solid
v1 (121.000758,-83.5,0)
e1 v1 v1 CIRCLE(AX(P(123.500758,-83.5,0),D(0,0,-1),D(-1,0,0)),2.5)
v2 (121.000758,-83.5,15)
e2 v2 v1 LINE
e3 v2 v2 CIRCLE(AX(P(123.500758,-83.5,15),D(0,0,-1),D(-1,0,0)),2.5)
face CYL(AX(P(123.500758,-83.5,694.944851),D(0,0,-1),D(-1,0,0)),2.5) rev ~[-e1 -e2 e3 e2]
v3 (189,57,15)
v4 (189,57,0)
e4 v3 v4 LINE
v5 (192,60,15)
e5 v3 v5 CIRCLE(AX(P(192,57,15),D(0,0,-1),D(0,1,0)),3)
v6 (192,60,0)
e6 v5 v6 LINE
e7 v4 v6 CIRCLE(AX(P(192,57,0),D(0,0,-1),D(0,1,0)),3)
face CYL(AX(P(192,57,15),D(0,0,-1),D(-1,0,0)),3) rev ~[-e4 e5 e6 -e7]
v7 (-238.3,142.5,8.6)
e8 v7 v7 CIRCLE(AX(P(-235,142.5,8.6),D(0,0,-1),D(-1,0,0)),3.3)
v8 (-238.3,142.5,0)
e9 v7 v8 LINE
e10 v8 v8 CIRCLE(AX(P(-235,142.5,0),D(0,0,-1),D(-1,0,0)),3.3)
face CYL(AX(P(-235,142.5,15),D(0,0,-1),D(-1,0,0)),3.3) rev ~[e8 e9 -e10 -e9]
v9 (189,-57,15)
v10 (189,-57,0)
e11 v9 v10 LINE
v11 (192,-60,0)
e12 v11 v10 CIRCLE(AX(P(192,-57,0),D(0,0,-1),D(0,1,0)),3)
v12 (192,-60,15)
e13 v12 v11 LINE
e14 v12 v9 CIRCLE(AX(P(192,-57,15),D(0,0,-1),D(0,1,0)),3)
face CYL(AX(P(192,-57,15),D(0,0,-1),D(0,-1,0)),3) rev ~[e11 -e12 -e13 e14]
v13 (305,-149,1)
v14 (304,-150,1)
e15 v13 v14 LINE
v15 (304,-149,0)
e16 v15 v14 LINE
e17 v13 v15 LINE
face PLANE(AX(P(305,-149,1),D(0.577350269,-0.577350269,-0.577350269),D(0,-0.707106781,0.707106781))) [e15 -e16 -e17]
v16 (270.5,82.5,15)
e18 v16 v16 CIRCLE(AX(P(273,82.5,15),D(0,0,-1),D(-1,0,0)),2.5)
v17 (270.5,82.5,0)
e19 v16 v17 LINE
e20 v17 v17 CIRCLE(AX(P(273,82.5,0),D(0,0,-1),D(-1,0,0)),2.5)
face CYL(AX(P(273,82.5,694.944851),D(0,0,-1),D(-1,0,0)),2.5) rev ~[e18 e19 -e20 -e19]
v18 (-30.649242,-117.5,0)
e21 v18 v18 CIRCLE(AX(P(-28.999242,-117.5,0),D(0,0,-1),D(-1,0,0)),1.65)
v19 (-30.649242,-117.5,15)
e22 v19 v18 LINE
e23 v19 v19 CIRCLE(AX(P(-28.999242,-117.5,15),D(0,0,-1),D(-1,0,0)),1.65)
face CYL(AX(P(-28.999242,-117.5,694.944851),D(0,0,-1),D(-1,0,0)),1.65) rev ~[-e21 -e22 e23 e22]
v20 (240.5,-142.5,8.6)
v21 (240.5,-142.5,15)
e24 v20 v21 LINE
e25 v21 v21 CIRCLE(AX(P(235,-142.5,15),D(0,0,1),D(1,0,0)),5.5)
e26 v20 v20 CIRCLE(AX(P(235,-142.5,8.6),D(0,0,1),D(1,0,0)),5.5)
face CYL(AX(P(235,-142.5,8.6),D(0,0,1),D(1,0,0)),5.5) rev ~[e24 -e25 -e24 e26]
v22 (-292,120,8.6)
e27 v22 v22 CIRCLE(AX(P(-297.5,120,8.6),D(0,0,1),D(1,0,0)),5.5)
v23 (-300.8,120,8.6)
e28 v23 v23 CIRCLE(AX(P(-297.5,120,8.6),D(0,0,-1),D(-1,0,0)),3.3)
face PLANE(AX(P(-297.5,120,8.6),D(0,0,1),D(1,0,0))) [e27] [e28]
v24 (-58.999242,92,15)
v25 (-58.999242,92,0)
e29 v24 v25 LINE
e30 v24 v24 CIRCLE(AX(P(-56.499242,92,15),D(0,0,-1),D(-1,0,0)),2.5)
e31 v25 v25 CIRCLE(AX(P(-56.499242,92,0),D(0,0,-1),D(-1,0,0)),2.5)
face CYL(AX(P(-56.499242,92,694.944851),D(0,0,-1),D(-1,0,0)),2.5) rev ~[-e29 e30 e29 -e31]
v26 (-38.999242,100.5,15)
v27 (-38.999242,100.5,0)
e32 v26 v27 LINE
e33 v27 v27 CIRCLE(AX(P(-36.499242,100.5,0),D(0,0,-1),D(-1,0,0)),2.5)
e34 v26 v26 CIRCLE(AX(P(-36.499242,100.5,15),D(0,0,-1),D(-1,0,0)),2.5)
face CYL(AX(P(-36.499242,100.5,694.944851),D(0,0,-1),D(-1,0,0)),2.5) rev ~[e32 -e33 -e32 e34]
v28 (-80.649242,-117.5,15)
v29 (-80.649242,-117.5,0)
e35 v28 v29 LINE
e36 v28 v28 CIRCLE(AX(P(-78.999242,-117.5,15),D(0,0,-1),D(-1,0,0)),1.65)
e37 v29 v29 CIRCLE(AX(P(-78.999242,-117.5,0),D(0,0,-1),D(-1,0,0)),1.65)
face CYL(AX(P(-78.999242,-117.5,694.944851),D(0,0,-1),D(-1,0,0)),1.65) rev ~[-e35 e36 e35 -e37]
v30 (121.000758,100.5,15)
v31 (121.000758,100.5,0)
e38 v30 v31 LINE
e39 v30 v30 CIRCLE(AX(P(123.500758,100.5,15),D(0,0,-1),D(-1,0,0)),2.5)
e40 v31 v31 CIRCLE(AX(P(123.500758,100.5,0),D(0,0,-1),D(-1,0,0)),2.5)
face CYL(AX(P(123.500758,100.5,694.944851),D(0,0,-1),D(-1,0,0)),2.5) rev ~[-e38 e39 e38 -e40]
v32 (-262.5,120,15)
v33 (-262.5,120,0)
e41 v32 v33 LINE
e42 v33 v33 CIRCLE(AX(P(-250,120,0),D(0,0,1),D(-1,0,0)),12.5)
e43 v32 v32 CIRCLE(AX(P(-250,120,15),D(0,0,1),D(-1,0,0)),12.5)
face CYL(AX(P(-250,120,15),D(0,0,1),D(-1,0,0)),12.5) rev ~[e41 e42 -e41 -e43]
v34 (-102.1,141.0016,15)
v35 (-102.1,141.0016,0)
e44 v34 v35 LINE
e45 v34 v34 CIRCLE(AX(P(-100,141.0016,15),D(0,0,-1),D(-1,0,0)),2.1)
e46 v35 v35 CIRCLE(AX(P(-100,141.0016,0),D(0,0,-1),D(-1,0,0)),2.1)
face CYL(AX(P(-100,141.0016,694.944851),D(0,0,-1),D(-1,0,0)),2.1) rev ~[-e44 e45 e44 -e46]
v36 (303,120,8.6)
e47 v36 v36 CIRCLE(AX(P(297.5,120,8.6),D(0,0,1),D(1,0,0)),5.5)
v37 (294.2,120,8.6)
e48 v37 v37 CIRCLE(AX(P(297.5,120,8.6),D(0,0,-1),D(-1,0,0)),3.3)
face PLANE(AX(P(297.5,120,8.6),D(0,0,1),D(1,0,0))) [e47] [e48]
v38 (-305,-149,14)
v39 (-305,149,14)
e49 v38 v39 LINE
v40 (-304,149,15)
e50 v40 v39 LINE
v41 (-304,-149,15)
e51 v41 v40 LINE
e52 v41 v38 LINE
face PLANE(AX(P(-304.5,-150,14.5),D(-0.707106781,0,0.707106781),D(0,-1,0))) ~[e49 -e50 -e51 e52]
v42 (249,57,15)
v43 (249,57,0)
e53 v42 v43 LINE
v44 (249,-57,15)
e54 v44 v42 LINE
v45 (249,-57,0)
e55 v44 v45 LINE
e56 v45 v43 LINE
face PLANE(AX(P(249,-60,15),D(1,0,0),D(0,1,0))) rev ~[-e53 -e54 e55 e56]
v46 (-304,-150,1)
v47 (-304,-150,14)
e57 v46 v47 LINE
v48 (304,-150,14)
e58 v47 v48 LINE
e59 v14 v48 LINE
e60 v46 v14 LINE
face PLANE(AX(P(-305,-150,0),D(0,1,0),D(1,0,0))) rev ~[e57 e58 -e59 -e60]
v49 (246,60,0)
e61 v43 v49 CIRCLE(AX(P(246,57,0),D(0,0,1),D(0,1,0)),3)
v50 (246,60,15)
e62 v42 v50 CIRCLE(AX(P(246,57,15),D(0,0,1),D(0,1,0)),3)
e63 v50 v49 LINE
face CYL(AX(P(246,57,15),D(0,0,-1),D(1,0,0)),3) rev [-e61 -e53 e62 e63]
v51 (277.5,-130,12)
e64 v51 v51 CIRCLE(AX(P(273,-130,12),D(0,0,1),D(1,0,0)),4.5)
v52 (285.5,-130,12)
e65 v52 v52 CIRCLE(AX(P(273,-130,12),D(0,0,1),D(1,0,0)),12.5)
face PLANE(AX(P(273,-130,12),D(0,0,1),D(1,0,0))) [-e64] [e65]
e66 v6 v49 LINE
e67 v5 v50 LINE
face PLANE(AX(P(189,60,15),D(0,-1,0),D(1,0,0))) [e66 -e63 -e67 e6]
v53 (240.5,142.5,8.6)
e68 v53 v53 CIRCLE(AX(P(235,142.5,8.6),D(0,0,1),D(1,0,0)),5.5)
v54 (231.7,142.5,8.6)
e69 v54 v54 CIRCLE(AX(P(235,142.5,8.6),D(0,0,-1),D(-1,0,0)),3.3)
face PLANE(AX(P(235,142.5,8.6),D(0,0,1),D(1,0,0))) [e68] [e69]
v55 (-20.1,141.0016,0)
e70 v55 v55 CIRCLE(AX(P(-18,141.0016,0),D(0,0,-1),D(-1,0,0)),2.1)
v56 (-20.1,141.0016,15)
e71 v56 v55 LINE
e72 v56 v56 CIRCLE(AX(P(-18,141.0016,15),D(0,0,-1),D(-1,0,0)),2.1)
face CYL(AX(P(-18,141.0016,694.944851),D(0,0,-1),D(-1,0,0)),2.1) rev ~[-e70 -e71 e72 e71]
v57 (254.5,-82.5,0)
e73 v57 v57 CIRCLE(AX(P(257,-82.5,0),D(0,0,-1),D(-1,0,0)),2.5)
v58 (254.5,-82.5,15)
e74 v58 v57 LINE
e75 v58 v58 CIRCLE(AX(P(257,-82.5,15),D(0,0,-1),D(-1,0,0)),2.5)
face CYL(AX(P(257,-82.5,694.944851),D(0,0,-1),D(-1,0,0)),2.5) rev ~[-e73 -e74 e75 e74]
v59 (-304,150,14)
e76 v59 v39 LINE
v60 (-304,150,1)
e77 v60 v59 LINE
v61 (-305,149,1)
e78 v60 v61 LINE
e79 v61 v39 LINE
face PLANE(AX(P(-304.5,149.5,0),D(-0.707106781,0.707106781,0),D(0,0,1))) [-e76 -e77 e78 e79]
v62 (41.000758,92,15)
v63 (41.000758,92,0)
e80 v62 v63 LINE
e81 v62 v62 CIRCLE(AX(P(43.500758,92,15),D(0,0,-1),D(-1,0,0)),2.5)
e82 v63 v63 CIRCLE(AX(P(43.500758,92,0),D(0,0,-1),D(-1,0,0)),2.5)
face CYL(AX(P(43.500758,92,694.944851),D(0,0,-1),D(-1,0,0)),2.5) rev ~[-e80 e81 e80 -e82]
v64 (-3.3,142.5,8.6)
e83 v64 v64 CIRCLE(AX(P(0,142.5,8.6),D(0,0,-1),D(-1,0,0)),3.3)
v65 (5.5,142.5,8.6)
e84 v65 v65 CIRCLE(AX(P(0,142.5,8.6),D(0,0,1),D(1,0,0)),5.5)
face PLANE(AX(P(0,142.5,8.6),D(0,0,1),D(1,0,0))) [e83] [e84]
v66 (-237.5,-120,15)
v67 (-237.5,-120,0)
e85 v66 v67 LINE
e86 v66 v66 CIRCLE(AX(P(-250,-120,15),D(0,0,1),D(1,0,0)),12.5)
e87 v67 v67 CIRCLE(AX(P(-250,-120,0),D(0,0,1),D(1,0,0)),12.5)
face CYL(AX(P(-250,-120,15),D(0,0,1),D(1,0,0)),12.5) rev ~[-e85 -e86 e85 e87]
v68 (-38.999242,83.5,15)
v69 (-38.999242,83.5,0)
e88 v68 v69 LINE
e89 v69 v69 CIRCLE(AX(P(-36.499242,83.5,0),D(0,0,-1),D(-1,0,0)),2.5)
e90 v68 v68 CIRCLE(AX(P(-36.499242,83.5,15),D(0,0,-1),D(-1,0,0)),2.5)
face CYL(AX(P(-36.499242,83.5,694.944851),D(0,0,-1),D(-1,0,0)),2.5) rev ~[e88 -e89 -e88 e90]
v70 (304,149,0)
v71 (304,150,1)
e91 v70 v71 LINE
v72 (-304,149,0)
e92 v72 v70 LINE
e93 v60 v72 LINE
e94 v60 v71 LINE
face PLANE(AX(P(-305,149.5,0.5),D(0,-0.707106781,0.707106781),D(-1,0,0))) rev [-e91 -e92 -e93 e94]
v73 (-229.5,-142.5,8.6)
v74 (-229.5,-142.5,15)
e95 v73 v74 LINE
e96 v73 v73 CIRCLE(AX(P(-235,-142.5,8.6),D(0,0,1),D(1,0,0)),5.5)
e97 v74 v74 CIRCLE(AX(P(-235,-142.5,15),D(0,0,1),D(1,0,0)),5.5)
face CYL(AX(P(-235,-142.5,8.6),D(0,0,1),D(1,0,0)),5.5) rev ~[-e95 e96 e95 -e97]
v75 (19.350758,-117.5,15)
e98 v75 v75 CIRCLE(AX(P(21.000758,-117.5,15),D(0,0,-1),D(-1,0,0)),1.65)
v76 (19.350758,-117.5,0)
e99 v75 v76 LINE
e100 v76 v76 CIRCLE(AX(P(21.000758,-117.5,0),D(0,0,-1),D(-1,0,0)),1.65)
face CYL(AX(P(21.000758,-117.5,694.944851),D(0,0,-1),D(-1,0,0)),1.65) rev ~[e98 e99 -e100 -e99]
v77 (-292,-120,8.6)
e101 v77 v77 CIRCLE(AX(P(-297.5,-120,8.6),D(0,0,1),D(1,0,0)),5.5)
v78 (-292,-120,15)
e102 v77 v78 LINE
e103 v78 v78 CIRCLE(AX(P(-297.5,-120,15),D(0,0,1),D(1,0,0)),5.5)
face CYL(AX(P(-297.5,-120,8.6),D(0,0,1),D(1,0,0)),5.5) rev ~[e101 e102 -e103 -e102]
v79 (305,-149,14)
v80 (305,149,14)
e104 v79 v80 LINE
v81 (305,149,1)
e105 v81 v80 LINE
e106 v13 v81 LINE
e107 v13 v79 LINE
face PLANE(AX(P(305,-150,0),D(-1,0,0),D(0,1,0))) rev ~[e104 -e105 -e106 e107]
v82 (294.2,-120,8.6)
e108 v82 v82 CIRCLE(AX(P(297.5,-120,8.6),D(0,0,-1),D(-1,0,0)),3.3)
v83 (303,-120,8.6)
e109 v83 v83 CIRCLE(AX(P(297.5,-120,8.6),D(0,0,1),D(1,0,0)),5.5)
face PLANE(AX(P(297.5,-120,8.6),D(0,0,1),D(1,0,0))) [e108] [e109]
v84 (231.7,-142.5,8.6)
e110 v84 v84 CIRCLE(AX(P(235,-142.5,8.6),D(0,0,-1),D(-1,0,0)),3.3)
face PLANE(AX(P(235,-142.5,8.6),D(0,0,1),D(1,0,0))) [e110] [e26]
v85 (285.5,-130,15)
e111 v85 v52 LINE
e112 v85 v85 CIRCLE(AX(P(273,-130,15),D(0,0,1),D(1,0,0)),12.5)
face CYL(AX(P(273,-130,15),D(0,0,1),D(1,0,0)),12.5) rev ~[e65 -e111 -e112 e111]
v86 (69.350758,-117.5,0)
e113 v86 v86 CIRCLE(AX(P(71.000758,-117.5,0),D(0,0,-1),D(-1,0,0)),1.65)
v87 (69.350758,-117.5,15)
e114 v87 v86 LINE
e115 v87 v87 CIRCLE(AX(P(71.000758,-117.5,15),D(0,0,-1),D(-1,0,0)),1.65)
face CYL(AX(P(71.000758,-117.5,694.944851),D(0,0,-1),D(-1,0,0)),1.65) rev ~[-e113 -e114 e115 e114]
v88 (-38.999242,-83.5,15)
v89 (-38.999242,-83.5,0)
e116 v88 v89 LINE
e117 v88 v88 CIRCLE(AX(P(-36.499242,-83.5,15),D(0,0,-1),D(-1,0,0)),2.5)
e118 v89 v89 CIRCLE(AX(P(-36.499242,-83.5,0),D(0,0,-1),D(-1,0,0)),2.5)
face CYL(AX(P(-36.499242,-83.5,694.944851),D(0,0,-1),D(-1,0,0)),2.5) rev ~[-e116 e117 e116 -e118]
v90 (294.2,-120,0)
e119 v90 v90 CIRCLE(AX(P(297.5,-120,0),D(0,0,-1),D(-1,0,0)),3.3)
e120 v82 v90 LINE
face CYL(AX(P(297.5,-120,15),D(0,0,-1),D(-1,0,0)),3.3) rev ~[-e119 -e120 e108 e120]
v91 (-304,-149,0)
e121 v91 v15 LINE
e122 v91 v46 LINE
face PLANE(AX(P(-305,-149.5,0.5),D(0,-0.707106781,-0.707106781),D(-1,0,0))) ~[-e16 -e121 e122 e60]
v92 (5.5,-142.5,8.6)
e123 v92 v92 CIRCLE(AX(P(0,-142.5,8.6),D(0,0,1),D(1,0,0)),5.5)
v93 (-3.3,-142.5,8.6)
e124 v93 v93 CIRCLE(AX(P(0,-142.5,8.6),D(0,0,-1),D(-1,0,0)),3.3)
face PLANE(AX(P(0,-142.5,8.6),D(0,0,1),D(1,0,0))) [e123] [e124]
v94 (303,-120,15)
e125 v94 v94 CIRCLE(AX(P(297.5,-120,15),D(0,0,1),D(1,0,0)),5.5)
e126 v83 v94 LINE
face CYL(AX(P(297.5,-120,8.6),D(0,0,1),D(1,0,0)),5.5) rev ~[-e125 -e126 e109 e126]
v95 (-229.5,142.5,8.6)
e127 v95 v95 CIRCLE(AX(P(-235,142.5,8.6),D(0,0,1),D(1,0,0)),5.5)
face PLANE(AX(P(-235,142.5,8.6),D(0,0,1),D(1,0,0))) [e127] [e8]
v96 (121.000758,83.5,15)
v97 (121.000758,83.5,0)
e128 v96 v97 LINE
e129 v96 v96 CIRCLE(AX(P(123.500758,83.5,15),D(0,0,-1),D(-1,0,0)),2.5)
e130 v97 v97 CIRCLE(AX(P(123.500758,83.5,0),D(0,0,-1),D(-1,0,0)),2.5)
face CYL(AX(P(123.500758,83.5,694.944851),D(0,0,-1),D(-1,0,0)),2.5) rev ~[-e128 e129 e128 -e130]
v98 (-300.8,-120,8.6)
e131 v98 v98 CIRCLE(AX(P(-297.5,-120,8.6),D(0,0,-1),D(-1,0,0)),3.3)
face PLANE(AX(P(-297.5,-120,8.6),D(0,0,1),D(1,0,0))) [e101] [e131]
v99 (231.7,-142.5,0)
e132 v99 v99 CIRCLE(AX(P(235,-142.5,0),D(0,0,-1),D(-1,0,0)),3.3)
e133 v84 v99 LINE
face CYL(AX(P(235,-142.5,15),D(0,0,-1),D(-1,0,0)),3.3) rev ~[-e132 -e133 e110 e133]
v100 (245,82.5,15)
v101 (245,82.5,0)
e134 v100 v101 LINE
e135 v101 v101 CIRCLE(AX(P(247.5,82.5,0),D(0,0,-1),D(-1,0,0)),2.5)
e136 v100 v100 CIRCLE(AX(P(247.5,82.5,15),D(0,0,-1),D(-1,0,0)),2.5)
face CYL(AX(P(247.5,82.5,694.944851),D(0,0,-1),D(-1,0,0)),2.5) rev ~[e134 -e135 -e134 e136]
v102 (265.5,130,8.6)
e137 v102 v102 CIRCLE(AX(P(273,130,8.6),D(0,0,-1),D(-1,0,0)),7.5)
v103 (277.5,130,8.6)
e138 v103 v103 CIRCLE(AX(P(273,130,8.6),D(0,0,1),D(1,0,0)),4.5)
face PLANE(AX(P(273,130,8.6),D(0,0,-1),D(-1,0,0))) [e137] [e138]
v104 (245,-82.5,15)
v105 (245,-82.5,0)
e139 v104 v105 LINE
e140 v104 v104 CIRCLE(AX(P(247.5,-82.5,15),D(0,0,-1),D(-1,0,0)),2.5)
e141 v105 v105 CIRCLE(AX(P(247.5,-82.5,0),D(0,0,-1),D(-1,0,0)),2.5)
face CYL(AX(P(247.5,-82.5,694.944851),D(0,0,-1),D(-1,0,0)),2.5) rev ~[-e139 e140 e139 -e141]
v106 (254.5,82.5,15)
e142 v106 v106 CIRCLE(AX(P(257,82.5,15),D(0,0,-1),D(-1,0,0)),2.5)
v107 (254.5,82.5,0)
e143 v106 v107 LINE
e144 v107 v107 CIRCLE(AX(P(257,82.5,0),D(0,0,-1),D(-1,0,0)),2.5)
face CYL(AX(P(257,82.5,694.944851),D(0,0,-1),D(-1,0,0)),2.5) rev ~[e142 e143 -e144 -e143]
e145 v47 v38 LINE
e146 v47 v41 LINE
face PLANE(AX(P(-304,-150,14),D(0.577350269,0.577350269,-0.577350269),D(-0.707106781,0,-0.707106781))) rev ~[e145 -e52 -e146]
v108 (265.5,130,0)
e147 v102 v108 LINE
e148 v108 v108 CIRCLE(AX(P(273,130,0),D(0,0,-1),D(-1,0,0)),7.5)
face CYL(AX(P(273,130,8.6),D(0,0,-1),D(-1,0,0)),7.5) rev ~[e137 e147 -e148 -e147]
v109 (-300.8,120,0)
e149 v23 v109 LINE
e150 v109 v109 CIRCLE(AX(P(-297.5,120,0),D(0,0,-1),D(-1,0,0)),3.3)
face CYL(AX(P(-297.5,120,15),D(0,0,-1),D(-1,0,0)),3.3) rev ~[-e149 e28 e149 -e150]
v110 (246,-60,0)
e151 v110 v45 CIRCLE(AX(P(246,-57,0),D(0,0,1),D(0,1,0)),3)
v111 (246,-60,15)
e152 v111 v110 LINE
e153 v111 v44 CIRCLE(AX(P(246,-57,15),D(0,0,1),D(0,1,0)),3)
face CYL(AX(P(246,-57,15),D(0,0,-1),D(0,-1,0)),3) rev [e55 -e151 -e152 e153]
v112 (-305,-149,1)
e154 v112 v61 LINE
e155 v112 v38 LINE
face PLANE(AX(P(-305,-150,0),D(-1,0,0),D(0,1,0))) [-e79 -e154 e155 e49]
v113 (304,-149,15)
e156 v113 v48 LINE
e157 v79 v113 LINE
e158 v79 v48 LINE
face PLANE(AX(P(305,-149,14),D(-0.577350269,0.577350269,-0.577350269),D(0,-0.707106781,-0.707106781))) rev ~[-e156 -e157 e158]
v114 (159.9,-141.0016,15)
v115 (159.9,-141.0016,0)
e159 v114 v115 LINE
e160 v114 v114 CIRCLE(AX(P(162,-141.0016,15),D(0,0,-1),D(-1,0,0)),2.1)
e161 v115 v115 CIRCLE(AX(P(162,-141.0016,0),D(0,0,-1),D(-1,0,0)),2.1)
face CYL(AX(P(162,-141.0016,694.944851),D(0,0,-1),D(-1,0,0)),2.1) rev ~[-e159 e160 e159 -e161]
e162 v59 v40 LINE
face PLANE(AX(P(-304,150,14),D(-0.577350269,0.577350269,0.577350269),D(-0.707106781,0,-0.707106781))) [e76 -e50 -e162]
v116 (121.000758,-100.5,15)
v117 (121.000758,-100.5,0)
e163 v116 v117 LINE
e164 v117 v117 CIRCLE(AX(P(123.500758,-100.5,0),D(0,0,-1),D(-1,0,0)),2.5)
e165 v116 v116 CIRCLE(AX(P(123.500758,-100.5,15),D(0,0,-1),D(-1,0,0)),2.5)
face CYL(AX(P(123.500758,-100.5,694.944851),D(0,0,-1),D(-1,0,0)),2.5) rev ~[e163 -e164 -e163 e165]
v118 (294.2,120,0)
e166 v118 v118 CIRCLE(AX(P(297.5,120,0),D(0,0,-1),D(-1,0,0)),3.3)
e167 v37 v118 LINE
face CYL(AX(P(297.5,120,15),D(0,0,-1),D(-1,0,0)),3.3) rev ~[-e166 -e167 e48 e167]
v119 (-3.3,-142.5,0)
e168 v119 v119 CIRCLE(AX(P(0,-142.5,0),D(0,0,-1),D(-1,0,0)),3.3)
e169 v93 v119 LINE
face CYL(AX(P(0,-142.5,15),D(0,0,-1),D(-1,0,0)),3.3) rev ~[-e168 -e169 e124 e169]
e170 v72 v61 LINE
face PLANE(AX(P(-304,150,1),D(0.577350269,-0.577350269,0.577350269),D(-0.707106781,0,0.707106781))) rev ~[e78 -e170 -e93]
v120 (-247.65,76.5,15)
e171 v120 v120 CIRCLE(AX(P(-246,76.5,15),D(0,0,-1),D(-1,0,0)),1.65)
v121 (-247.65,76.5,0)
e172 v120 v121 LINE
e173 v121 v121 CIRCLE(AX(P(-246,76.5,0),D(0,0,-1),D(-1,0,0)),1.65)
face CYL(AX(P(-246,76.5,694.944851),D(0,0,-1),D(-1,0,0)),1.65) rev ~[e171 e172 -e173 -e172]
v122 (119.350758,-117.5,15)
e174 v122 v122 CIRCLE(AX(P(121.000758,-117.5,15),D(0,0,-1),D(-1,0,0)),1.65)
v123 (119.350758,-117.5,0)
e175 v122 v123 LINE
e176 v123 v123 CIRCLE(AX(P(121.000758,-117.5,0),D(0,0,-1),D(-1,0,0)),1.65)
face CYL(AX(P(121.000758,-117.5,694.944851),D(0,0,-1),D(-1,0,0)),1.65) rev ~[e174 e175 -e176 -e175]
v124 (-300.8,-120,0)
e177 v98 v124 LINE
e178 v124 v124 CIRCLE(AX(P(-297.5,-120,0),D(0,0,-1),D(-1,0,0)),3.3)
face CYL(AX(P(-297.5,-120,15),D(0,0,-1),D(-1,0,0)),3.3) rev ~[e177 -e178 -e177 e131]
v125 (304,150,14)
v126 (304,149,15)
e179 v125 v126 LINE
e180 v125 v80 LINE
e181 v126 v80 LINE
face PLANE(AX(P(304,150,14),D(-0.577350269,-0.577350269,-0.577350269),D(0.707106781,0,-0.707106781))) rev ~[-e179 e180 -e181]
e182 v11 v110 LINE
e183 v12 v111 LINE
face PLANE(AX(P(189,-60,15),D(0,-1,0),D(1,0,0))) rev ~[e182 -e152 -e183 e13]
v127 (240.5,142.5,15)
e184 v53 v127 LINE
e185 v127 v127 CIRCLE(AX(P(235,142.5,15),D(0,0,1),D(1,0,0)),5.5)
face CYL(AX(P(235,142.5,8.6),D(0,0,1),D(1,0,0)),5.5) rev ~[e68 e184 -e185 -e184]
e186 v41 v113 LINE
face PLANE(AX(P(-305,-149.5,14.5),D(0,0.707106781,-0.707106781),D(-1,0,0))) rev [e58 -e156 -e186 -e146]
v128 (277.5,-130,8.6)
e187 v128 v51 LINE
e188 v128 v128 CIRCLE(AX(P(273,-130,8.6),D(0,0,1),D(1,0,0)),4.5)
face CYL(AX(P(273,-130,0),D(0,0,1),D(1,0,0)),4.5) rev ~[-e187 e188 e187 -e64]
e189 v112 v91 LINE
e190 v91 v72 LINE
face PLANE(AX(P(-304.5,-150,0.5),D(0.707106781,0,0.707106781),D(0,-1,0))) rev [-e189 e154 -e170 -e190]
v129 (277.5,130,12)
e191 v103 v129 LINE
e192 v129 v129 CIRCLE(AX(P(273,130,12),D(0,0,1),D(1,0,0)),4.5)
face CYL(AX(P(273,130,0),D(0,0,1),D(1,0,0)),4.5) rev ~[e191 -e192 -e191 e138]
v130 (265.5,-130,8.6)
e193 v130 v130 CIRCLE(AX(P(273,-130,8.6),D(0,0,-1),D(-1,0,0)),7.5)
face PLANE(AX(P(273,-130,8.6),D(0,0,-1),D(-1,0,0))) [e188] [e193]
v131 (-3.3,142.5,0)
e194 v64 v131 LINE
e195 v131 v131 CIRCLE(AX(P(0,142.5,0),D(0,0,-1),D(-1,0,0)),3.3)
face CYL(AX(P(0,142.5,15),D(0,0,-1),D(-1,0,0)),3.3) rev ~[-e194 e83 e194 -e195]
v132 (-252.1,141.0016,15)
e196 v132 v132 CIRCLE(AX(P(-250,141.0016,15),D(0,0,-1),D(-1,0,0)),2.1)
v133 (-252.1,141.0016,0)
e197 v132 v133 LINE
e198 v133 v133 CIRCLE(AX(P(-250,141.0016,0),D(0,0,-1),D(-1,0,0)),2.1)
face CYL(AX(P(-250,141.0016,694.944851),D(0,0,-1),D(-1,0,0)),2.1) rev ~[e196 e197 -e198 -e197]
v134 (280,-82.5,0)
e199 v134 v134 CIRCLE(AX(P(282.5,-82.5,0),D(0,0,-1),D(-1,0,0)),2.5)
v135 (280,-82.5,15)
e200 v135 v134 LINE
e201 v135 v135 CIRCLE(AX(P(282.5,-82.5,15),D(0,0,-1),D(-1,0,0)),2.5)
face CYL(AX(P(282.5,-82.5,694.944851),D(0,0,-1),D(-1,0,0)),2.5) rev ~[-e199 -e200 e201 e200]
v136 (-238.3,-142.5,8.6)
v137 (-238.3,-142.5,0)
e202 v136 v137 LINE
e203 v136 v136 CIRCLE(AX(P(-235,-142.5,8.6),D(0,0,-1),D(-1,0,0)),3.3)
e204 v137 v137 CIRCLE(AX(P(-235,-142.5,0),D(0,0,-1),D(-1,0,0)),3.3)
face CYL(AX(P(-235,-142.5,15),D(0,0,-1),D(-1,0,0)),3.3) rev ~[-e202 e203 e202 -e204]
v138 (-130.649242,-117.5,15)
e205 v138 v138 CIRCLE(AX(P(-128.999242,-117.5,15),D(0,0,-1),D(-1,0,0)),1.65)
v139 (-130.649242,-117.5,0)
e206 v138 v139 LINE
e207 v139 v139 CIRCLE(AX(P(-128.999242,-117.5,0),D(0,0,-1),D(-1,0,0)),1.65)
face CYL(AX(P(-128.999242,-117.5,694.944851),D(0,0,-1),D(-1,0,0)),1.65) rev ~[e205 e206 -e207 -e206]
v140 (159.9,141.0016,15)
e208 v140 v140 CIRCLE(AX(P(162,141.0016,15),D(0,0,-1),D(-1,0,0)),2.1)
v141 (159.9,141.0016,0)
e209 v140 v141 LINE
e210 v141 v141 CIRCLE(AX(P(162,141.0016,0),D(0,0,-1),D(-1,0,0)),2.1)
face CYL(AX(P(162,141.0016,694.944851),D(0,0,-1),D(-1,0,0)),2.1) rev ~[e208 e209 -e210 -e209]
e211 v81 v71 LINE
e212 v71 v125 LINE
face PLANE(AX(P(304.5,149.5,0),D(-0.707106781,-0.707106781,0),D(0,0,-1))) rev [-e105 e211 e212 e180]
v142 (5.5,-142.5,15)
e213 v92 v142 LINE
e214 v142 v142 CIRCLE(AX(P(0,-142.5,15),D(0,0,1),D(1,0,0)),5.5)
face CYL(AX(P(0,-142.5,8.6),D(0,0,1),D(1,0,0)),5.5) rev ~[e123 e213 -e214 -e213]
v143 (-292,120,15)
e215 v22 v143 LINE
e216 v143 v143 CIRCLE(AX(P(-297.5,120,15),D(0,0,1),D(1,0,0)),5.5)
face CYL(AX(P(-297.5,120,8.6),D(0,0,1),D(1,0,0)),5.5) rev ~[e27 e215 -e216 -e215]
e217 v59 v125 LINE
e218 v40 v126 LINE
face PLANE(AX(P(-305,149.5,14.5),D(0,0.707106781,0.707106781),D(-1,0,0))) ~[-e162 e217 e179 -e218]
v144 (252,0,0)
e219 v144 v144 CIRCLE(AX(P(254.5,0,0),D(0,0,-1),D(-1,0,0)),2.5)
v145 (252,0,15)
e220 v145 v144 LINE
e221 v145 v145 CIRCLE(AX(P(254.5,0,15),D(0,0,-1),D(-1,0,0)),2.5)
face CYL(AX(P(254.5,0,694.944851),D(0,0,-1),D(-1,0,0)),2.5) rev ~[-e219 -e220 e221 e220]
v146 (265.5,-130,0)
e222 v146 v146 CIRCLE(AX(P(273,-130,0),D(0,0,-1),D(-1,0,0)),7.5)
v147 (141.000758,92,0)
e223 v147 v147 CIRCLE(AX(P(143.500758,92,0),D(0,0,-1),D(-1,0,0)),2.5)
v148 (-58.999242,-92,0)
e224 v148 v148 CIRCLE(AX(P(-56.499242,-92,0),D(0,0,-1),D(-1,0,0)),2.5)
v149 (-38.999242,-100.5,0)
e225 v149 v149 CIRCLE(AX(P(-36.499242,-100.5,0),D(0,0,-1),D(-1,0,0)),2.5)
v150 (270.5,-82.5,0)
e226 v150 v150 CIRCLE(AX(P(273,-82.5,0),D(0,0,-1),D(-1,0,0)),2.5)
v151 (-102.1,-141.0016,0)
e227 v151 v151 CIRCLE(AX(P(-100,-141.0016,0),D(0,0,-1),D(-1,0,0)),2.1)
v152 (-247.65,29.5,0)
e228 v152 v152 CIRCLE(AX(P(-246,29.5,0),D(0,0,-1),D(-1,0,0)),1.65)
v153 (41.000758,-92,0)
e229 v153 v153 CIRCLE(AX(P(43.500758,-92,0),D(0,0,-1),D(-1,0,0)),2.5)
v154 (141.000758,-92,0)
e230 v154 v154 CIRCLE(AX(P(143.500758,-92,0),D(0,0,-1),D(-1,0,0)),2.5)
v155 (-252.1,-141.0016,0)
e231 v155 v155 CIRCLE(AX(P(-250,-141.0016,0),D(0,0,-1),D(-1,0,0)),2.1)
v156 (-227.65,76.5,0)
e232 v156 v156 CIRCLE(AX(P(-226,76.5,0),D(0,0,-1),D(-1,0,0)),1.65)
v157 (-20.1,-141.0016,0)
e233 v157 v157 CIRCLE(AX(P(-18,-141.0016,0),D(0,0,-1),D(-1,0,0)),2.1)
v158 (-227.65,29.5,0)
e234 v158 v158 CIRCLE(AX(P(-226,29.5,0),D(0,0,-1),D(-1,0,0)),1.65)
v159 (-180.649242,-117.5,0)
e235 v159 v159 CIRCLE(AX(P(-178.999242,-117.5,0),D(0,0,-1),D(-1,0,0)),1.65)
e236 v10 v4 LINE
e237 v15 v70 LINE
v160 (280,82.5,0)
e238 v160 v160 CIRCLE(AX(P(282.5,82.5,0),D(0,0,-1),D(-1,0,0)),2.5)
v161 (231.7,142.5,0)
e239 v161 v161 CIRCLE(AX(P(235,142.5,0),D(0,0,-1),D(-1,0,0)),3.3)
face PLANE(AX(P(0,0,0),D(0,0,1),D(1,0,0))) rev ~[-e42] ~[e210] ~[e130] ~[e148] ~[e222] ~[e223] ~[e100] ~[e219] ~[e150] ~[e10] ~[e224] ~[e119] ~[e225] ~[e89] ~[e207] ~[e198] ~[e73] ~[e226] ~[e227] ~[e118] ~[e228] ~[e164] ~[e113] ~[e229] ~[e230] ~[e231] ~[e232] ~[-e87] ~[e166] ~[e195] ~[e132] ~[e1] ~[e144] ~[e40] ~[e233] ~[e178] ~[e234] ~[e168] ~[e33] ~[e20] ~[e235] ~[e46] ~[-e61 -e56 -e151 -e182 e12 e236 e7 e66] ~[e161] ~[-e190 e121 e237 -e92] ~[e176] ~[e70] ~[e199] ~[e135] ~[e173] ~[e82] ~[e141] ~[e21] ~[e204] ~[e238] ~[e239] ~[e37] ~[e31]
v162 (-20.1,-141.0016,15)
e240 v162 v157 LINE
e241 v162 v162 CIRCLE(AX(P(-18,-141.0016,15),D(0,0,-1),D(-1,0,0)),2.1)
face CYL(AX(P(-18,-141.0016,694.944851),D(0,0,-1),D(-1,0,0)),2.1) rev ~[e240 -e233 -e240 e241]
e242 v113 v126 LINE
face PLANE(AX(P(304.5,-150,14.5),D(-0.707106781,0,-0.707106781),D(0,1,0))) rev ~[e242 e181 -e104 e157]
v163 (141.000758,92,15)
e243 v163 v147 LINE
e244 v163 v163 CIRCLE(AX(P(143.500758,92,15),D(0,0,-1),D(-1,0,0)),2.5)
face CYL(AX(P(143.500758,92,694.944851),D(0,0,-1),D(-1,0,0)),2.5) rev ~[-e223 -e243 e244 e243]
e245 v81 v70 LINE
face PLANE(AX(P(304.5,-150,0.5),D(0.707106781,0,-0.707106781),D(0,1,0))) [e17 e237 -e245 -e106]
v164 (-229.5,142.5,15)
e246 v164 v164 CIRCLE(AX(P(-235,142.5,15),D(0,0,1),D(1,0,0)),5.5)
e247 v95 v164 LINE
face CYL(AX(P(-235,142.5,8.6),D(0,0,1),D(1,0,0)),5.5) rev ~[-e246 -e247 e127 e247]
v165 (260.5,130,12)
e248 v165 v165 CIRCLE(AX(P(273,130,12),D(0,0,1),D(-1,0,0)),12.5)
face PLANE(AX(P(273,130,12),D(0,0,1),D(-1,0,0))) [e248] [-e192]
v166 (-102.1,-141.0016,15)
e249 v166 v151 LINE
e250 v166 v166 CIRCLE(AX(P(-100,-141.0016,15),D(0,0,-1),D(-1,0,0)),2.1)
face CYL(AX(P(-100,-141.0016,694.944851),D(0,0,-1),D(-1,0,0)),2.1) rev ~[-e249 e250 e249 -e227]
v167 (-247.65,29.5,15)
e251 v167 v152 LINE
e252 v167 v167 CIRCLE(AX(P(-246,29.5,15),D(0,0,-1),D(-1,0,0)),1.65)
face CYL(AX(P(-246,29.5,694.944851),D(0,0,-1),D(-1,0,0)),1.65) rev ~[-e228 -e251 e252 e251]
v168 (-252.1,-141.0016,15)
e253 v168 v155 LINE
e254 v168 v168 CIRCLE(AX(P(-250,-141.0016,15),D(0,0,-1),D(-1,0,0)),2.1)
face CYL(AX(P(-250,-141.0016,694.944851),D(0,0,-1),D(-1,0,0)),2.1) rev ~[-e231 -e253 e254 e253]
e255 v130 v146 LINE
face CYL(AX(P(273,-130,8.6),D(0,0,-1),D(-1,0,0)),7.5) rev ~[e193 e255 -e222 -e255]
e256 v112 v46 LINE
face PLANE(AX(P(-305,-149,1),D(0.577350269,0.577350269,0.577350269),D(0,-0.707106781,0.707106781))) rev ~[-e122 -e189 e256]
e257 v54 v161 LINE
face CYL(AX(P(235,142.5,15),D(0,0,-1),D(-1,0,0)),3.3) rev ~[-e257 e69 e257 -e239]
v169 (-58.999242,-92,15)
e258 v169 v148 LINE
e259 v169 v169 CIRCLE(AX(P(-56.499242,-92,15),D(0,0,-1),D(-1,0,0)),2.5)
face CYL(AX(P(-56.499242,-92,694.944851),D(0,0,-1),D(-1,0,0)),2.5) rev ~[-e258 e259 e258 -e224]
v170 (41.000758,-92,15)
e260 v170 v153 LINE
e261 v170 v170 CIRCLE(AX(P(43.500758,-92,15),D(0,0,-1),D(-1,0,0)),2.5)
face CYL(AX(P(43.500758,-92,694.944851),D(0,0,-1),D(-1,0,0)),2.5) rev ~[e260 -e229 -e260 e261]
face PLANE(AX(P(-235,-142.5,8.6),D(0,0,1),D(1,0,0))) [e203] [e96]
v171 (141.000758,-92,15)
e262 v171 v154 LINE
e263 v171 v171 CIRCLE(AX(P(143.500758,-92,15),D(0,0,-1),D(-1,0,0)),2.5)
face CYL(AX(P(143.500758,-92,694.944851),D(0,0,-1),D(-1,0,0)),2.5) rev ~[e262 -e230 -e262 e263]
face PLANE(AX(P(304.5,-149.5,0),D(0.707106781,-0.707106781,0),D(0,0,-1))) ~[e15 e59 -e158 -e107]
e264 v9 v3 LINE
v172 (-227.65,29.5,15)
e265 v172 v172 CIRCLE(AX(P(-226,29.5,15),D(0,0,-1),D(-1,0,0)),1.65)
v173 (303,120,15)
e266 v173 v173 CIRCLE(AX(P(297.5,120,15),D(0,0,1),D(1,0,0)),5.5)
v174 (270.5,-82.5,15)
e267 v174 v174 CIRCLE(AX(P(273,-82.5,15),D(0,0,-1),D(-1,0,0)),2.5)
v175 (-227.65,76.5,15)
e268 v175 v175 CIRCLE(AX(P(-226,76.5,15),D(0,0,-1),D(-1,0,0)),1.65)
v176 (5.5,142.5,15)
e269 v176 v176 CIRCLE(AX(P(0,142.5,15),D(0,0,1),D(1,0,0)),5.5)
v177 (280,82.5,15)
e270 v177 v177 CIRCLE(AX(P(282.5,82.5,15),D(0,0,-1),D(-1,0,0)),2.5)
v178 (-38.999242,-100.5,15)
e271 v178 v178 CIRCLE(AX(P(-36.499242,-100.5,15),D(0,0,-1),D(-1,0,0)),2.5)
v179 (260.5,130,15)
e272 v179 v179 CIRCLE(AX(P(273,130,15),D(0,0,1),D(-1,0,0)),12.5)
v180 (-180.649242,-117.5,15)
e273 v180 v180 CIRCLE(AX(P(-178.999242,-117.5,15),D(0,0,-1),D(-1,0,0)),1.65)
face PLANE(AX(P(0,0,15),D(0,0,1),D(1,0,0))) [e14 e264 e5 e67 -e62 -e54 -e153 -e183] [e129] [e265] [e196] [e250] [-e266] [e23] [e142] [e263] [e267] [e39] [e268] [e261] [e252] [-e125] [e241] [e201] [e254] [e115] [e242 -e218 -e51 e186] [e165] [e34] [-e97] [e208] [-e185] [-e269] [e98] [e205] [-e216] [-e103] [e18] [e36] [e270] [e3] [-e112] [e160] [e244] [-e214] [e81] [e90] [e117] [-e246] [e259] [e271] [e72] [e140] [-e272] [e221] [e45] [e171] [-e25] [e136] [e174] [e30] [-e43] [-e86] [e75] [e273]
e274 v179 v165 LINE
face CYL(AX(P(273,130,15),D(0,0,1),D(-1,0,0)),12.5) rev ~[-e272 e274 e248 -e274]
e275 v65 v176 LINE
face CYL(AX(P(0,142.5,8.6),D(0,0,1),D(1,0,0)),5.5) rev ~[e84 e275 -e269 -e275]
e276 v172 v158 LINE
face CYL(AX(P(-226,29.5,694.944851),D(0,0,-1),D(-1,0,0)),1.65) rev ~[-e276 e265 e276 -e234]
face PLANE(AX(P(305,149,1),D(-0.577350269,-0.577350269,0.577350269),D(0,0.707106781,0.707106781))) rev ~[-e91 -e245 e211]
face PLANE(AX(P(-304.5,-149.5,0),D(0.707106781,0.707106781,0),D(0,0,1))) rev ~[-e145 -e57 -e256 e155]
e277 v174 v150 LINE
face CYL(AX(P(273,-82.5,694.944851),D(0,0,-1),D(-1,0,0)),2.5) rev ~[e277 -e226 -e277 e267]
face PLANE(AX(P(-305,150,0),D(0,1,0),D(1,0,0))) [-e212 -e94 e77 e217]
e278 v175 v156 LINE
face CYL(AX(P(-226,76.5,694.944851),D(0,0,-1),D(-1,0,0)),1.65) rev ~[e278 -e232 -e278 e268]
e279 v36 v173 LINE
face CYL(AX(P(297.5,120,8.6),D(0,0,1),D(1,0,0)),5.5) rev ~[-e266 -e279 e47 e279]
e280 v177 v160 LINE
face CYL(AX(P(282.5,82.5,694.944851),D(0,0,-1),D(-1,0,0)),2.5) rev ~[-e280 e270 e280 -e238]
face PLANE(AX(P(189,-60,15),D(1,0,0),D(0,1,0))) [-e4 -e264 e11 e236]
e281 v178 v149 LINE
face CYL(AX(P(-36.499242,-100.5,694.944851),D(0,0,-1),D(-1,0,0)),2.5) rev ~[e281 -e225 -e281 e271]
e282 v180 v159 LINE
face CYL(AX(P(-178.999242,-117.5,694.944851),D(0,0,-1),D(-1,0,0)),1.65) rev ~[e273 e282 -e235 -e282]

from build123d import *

# Parameters (mm, degrees)
SKETCH_1_W                     = 610
SKETCH_1_H                     = 300
EXTRUDE_1_DEPTH                = 15
SKETCH_25_R                    = 12.5
CUT_EXTRUDE_4_DEPTH            = 3
SKETCH_26_W                    = 60
SKETCH_26_H                    = 120
CUT_EXTRUDE_5_DEPTH            = 341.220516724
HOLE_WIZARD_M6_1_D             = 5
MM_1_D                         = 5
HOLE_WIZARD_M8_1_D             = 9
HOLE_WIZARD_M8_1_CBORE_D       = 15
HOLE_WIZARD_M8_1_CBORE_DEPTH   = 8.6
MM_0_D                         = 5
HOLE_WIZARD_M6_2_D             = 5
HOLE_WIZARD_M6_1_2_D           = 6.6
HOLE_WIZARD_M6_1_2_CBORE_D     = 11
HOLE_WIZARD_M6_1_2_CBORE_DEPTH = 6.4
HOLE_WIZARD_M4_1_D             = 3.3
PATTERN_LINEAR_1_COUNT         = 7
PATTERN_LINEAR_1_PITCH         = 50
HOLE_WIZARD_M5_1_D             = 4.2
SKETCH_46_R                    = 12.5
CUT_EXTRUDE_6_DEPTH            = 341.220516724
CHAMFER_1_SIZE                 = 1
HOLE_WIZARD_M4_2_D             = 3.3
FILLET_1_R                     = 3


with BuildPart() as part:
    # 草图1 → 凸台-拉伸1 (new body)
    with BuildSketch(Plane.XY):
        Rectangle(SKETCH_1_W, SKETCH_1_H)
    extrude(amount=EXTRUDE_1_DEPTH)

    # 草图25 → 切除-拉伸4 (cut)
    with BuildSketch(Plane.XY.offset(15)):
        with Locations((273, -130)):
            Circle(SKETCH_25_R)
        with Locations(Location((273, 130, 0), (0, 0, 180))):
            Circle(SKETCH_25_R)
    extrude(amount=-CUT_EXTRUDE_4_DEPTH, mode=Mode.SUBTRACT)

    # 草图26 → 切除-拉伸5 (cut, through all)
    with BuildSketch(Plane.XY.offset(15)):
        with Locations((219, 0)):
            Rectangle(SKETCH_26_W, SKETCH_26_H)
    extrude(amount=-CUT_EXTRUDE_5_DEPTH, mode=Mode.SUBTRACT)

    # Hole Wizard M6 _1 (through all)
    with Locations(Plane.XY.offset(15)):
        with Locations((143.500757595, -92), (-56.499242405, -92), (-56.499242405, 92), (143.500757595, 92)):
            Hole(HOLE_WIZARD_M6_1_D / 2)

    # 大小mm 暗销孔1 (through all)
    with Locations(Plane.XY.offset(15)):
        with Locations((123.500757595, -83.5), (123.500757595, -100.5), (43.500757595, -92), (-36.499242405, -100.5), (-36.499242405, -83.5), (-36.499242405, 83.5), (-36.499242405, 100.5), (123.500757595, 100.5), (123.500757595, 83.5), (43.500757595, 92)):
            Hole(MM_1_D / 2)

    # M8 六角凹头螺钉的柱形沉头孔1 (through all)
    with Locations(Plane(origin=(0, 0, 0), x_dir=(-1, 0, 0), z_dir=(0, 0, -1))):
        with Locations((-273, -130), (-273, 130)):
            CounterBoreHole(HOLE_WIZARD_M8_1_D / 2, HOLE_WIZARD_M8_1_CBORE_D / 2, HOLE_WIZARD_M8_1_CBORE_DEPTH)

    # 大小mm 暗销孔0 (through all)
    with Locations(Plane.XY.offset(15)):
        with Locations((282.5, -82.5), (282.5, 82.5), (247.5, 82.5), (247.5, -82.5), (254.5, 0)):
            Hole(MM_0_D / 2)

    # M6 螺纹孔2 (through all)
    with Locations(Plane.XY.offset(15)):
        with Locations((257, -82.5), (273, -82.5), (257, 82.5), (273, 82.5)):
            Hole(HOLE_WIZARD_M6_2_D / 2)

    # Hole Wizard M6 _1 2 (through all)
    with Locations(Plane.XY.offset(15)):
        with Locations((-297.5, -120), (-235, -142.5), (-235, 142.5), (-297.5, 120), (297.5, 120), (235, 142.5), (235, -142.5), (297.5, -120), (0, -142.5), (0, 142.5)):
            CounterBoreHole(HOLE_WIZARD_M6_1_2_D / 2, HOLE_WIZARD_M6_1_2_CBORE_D / 2, HOLE_WIZARD_M6_1_2_CBORE_DEPTH)

    # M4 螺纹孔1 (through all)
    with Locations(Plane.XY.offset(15)):
        with Locations((121.000757595, -117.5)):
            hole_wizard_m4_1 = Hole(HOLE_WIZARD_M4_1_D / 2)

    # 阵列(线性)1: M4 螺纹孔1 ×7
    with Locations(*[(-i * PATTERN_LINEAR_1_PITCH, 0, 0) for i in range(1, PATTERN_LINEAR_1_COUNT)]):
        add(hole_wizard_m4_1, mode=Mode.SUBTRACT)

    # M5 螺纹孔1 (through all)
    with Locations(Plane.XY.offset(15)):
        with Locations((-100, -141.0016), (-250, -141.0016), (-250, 141.0016), (-100, 141.0016), (-18, 141.0016), (162.000000007, 141.0016), (162.000000007, -141.0016), (-18, -141.0016)):
            Hole(HOLE_WIZARD_M5_1_D / 2)

    # 草图46 → 切除-拉伸6 (cut, through all)
    with BuildSketch(Plane.XY.offset(15)):
        with Locations((-250, -120)):
            Circle(SKETCH_46_R)
        with Locations(Location((-250, 120, 0), (0, 0, 180))):
            Circle(SKETCH_46_R)
    extrude(amount=-CUT_EXTRUDE_6_DEPTH, mode=Mode.SUBTRACT)

    # 倒角1
    chamfer_1_edges = [part.edges().sort_by_distance(p)[0] for p in [
        (-305, 0, 15),
        (0, -150, 15),
        (305, 0, 15),
        (0, -150, 0),
        (-305, 0, 0),
        (0, 150, 0),
        (305, 0, 0),
        (0, 150, 15),
        (305, -150, 7.5),
        (-305, -150, 7.5),
        (-305, 150, 7.5),
        (305, 150, 7.5),
    ]]
    chamfer(chamfer_1_edges, length=CHAMFER_1_SIZE)

    # M4 螺纹孔2 (through all)
    with Locations(Plane.XY.offset(15)):
        with Locations((-246, 76.5), (-226, 76.5), (-246, 29.5), (-226, 29.5)):
            Hole(HOLE_WIZARD_M4_2_D / 2)

    # 圆角1
    fillet_1_edges = [part.edges().sort_by_distance(p)[0] for p in [
        (189, -60, 7.5),
        (189, 60, 7.5),
        (249, 60, 7.5),
        (249, -60, 7.5),
    ]]
    fillet(fillet_1_edges, radius=FILLET_1_R)


solid = part.part
